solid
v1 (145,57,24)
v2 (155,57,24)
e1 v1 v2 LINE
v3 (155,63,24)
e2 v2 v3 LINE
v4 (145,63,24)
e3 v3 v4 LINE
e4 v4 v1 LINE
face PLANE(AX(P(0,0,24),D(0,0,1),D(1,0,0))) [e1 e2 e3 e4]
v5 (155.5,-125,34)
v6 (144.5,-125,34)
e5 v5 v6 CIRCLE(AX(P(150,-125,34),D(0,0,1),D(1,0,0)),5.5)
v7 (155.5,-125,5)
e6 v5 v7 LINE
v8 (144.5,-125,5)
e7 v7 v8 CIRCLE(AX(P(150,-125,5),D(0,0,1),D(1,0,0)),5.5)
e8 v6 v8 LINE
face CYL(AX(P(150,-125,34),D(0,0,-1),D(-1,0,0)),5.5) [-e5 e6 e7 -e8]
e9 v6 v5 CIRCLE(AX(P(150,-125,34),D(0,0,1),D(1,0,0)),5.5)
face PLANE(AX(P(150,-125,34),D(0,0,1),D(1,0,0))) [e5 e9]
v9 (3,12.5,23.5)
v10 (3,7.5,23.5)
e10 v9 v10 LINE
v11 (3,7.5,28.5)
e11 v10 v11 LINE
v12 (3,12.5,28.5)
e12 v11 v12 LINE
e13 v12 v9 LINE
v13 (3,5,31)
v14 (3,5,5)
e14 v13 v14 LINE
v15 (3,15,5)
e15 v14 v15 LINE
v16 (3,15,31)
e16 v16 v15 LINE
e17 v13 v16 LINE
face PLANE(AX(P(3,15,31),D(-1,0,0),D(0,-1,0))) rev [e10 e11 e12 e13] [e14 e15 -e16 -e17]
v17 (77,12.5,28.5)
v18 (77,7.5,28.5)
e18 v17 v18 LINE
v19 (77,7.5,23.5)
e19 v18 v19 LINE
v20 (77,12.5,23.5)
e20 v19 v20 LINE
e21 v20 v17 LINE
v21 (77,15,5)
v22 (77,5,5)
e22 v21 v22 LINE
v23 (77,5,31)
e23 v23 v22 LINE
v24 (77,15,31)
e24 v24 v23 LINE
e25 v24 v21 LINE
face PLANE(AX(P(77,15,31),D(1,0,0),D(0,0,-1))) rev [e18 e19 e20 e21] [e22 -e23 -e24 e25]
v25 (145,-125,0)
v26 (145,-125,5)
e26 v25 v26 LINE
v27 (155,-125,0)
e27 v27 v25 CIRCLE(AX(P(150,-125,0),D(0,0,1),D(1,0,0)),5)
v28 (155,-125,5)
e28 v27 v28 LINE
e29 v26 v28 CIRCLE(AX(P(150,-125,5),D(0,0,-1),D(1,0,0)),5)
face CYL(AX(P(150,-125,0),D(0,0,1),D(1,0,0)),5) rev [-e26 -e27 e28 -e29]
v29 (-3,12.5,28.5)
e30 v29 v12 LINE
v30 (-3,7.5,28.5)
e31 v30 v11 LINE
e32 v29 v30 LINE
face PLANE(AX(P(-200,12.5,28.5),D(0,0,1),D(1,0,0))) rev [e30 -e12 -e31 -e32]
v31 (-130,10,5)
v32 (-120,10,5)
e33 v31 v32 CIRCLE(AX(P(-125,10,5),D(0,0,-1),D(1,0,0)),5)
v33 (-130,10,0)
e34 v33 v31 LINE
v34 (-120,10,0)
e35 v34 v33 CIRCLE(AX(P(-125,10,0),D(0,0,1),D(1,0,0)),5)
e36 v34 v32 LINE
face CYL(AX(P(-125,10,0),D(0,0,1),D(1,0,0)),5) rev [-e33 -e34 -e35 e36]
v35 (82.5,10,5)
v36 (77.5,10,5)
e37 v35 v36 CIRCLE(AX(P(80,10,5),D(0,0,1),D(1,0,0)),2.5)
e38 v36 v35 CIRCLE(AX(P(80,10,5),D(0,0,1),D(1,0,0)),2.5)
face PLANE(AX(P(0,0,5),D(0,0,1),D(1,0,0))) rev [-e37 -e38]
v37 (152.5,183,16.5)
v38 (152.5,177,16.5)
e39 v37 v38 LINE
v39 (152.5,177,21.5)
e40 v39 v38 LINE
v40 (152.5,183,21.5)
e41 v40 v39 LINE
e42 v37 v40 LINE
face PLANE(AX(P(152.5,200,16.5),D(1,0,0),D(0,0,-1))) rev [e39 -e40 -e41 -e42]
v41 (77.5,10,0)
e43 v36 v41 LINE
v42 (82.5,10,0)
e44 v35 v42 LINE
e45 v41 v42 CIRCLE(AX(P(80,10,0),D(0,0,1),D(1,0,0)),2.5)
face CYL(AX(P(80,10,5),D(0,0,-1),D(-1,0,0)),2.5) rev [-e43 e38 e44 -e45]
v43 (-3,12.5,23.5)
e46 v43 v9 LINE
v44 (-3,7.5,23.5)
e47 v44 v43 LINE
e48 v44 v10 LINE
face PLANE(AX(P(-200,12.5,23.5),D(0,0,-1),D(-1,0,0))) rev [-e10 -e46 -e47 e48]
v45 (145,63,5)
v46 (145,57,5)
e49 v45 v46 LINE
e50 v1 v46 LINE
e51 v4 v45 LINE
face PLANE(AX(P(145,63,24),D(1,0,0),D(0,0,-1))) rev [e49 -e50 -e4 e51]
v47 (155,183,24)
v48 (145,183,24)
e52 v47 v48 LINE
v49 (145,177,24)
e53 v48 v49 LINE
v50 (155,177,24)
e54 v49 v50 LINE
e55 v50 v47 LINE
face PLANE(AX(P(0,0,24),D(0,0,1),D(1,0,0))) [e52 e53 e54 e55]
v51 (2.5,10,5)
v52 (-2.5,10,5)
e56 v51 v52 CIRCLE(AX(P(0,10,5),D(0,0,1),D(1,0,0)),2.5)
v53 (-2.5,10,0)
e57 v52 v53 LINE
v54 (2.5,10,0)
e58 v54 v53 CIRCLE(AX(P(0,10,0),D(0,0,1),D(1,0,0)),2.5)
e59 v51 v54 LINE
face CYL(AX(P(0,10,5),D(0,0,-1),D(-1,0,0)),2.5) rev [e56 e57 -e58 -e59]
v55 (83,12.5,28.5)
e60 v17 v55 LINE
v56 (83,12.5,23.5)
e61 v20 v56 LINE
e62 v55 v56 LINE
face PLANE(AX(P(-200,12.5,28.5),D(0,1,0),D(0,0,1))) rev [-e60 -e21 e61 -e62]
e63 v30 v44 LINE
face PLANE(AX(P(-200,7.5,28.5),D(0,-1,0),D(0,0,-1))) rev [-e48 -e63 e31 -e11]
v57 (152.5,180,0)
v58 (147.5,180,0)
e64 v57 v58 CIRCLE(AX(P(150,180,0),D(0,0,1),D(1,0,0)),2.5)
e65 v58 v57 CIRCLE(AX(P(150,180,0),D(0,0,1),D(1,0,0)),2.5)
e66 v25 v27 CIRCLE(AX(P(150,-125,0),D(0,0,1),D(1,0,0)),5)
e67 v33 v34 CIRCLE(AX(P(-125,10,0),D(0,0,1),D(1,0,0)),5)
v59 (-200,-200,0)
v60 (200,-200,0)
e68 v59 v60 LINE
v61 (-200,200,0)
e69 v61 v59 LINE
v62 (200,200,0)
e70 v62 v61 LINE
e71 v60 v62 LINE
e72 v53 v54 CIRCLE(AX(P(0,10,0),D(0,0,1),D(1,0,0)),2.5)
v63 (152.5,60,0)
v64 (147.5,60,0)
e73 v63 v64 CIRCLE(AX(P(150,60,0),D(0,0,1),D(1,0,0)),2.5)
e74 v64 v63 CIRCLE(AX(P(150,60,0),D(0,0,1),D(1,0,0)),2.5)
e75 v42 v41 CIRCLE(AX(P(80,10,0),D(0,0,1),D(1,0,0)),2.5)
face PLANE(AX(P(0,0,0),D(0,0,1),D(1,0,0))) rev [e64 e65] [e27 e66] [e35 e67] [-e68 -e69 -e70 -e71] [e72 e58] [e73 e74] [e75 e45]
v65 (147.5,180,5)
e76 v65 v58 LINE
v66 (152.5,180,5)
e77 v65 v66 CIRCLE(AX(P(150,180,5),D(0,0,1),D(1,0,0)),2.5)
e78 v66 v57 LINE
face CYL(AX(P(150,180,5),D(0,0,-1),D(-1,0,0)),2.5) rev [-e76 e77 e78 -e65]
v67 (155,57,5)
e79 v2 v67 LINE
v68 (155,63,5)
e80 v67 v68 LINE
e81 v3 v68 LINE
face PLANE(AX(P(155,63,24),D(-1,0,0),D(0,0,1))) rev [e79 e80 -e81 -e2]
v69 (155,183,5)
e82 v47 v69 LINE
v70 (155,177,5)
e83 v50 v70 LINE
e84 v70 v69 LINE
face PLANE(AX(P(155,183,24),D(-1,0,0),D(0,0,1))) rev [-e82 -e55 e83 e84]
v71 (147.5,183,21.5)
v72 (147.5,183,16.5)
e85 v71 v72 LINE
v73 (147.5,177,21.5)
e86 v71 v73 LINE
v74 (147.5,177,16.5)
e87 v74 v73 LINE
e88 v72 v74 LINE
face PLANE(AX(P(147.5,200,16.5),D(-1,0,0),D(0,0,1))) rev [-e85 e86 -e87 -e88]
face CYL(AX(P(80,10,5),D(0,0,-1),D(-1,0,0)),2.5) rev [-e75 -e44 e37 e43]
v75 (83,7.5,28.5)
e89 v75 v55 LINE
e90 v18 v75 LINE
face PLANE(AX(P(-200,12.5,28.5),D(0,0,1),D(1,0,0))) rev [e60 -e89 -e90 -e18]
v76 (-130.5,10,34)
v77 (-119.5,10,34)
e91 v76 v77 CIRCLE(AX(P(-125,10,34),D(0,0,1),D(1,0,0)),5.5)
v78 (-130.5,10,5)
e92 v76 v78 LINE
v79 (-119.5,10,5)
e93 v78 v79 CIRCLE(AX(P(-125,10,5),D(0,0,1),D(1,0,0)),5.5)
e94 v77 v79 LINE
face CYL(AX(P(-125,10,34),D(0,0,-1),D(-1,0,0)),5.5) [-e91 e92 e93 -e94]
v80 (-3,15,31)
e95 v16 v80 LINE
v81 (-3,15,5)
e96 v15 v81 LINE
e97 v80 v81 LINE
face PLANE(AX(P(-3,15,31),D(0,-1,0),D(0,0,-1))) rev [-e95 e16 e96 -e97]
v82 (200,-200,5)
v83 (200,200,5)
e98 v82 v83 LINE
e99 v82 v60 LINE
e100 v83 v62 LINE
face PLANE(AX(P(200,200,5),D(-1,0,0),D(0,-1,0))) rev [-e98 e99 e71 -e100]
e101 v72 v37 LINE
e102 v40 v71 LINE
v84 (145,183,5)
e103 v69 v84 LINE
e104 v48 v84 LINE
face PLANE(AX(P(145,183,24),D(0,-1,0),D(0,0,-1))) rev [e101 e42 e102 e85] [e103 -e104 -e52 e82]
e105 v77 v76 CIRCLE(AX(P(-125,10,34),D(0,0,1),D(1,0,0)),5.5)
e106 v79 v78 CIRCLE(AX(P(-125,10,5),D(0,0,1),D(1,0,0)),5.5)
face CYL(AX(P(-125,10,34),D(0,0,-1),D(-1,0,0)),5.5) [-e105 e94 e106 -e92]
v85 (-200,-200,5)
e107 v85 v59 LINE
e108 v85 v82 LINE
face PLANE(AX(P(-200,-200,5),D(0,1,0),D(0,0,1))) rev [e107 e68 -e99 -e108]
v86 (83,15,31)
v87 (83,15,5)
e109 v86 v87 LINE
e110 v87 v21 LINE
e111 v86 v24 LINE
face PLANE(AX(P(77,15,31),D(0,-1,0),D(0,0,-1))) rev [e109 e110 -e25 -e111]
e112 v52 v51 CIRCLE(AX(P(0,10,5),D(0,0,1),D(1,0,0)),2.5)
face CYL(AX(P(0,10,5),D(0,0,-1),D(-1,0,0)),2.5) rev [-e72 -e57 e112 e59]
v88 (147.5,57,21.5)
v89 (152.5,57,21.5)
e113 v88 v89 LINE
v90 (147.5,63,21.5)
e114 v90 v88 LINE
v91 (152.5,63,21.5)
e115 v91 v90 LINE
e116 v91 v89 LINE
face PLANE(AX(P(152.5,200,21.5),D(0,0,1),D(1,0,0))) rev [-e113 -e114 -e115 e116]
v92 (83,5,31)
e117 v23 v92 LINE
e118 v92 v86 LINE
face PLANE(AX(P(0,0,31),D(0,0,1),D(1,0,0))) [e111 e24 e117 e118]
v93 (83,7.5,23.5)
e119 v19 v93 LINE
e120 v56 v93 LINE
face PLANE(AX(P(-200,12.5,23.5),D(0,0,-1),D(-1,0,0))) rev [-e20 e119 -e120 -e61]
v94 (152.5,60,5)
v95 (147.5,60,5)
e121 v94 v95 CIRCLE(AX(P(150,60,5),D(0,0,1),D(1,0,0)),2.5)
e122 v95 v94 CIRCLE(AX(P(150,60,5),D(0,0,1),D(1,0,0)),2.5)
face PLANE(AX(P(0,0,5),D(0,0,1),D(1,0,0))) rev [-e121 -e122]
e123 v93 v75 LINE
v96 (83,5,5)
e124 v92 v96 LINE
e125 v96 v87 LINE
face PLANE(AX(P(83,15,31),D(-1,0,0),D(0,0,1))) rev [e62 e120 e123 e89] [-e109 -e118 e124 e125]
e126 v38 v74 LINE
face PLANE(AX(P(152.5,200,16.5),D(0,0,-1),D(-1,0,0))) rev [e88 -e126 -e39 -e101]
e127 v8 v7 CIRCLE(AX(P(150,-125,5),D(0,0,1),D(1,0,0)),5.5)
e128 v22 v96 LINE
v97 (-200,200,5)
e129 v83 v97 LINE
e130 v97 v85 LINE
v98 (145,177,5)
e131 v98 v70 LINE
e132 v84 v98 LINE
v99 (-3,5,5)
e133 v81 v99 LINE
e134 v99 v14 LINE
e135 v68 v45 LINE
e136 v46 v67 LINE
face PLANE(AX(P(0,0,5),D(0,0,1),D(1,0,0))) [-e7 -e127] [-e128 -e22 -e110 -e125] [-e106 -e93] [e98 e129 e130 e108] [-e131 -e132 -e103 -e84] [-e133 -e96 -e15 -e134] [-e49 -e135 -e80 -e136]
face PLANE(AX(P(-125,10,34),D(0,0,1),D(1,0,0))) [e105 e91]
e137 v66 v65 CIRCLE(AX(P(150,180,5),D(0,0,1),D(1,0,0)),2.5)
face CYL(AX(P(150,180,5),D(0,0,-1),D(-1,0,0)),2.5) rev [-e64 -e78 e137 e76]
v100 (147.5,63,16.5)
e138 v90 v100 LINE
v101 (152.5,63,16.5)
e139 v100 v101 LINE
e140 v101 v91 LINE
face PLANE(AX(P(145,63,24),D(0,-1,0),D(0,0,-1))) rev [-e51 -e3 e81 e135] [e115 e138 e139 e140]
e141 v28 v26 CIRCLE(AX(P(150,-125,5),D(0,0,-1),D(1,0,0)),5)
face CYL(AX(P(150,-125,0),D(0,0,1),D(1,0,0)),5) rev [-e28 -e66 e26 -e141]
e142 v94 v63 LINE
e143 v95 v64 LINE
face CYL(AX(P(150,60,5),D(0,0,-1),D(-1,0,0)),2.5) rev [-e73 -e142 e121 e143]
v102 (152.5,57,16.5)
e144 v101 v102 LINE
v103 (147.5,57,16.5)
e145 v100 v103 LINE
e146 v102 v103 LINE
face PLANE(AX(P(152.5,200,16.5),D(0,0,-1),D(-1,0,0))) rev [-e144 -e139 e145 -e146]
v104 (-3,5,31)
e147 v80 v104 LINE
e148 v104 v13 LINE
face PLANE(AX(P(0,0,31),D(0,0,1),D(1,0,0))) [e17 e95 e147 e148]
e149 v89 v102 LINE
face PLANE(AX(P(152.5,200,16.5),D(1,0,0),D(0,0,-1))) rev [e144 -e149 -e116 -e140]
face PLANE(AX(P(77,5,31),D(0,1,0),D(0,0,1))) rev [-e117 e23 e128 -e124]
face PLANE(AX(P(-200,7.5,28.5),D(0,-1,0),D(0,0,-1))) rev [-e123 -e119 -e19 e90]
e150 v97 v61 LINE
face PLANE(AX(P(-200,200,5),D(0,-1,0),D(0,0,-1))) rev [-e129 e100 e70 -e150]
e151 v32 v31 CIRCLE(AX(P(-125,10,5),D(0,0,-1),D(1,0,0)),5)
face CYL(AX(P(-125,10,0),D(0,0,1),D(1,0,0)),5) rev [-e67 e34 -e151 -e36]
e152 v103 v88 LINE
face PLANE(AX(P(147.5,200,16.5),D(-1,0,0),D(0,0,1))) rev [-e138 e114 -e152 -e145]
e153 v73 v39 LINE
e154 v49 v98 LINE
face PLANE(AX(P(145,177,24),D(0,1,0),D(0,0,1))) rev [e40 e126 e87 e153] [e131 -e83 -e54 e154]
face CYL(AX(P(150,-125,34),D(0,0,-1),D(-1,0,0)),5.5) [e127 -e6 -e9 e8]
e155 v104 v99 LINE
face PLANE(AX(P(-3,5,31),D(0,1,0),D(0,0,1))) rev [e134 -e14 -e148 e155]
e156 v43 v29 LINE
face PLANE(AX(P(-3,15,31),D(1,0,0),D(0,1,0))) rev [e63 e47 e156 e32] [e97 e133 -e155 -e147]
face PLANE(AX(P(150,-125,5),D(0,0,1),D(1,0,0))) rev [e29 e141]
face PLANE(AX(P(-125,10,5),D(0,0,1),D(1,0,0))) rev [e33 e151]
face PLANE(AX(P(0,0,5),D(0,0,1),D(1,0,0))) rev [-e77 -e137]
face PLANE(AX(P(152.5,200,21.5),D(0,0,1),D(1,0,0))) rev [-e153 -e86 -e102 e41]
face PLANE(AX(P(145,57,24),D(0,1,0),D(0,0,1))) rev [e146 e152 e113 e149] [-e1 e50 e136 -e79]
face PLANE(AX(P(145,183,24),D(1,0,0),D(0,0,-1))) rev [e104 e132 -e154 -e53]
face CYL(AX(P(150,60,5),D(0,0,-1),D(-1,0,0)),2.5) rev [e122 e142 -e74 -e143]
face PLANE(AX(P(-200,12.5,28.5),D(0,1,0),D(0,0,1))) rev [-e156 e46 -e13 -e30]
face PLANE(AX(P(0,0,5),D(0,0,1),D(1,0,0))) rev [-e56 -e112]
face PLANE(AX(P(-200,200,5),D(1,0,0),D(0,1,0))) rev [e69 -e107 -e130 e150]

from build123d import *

# Parameters (mm, degrees)
SKETCH1_W               = 400
SKETCH1_H               = 400
SKETCH1_R               = 2.5
BOSS_EXTRUDE1_DEPTH     = 5
SKETCH4_R               = 5
CUT_EXTRUDE1_DEPTH      = 283.886903196
SKETCH6_W               = 6
SKETCH6_H               = 10
BOSS_EXTRUDE4_DEPTH     = 26
CUT_EXTRUDE2_DEPTH      = 348.922405142
CUT_EXTRUDE2_DEPTH_BACK = 348.922405142
SKETCH8_W               = 5
SKETCH8_H               = 5
SKETCH9_W               = 10
SKETCH9_H               = 6
BOSS_EXTRUDE5_DEPTH     = 19
CUT_EXTRUDE3_DEPTH      = 328.123829765
CUT_EXTRUDE3_DEPTH_BACK = 328.123829765
SKETCH10_W              = 5
SKETCH10_H              = 5
SKETCH11_R              = 5.5
BOSS_EXTRUDE7_DEPTH     = 29


with BuildPart() as part:
    # Sketch1 → Boss-Extrude1 (new body)
    with BuildSketch(Plane.XY):
        Rectangle(SKETCH1_W, SKETCH1_H)
        with Locations((0, 10)):
            Circle(SKETCH1_R, mode=Mode.SUBTRACT)
        with Locations((80, 10)):
            Circle(SKETCH1_R, mode=Mode.SUBTRACT)
        with Locations((150, 180)):
            Circle(SKETCH1_R, mode=Mode.SUBTRACT)
        with Locations((150, 60)):
            Circle(SKETCH1_R, mode=Mode.SUBTRACT)
    extrude(amount=BOSS_EXTRUDE1_DEPTH)

    # Sketch4 → Cut-Extrude1 (cut, through all)
    with BuildSketch(Plane.XY.offset(5)):
        with Locations((-125, 10)):
            Circle(SKETCH4_R)
        with Locations((150, -125)):
            Circle(SKETCH4_R)
    extrude(amount=-CUT_EXTRUDE1_DEPTH, mode=Mode.SUBTRACT)

    # Sketch6 → Boss-Extrude4 (add)
    with BuildSketch(Plane.XY.offset(5)):
        with Locations((0, 10)):
            Rectangle(SKETCH6_W, SKETCH6_H)
        with Locations((80, 10)):
            Rectangle(SKETCH6_W, SKETCH6_H)
    extrude(amount=BOSS_EXTRUDE4_DEPTH)

    # Sketch8 → Cut-Extrude2 (cut, two sides: drawn at the far end of the back side and taken through both)
    with BuildSketch(Plane(origin=(83, 0, 0), x_dir=(0, 0, -1), z_dir=(1, 0, 0)).offset(-CUT_EXTRUDE2_DEPTH_BACK)):
        with Locations((-26, 10)):
            Rectangle(SKETCH8_W, SKETCH8_H)
    extrude(amount=CUT_EXTRUDE2_DEPTH + CUT_EXTRUDE2_DEPTH_BACK, mode=Mode.SUBTRACT)

    # Sketch9 → Boss-Extrude5 (add)
    with BuildSketch(Plane.XY.offset(5)):
        with Locations((150, 180)):
            Rectangle(SKETCH9_W, SKETCH9_H)
        with Locations((150, 60)):
            Rectangle(SKETCH9_W, SKETCH9_H)
    extrude(amount=BOSS_EXTRUDE5_DEPTH)

    # Sketch10 → Cut-Extrude3 (cut, two sides: drawn at the far end of the back side and taken through both)
    with BuildSketch(Plane(origin=(0, 57, 0), x_dir=(-1, 0, 0), z_dir=(0, -1, 0)).offset(-CUT_EXTRUDE3_DEPTH_BACK)):
        with Locations((-150, -19)):
            Rectangle(SKETCH10_W, SKETCH10_H)
    extrude(amount=CUT_EXTRUDE3_DEPTH + CUT_EXTRUDE3_DEPTH_BACK, mode=Mode.SUBTRACT)

    # Sketch11 → Boss-Extrude7 (add)
    with BuildSketch(Plane.XY.offset(5)):
        with Locations((-125, 10)):
            Circle(SKETCH11_R)
        with Locations((150, -125)):
            Circle(SKETCH11_R)
    extrude(amount=BOSS_EXTRUDE7_DEPTH)


solid = part.part
